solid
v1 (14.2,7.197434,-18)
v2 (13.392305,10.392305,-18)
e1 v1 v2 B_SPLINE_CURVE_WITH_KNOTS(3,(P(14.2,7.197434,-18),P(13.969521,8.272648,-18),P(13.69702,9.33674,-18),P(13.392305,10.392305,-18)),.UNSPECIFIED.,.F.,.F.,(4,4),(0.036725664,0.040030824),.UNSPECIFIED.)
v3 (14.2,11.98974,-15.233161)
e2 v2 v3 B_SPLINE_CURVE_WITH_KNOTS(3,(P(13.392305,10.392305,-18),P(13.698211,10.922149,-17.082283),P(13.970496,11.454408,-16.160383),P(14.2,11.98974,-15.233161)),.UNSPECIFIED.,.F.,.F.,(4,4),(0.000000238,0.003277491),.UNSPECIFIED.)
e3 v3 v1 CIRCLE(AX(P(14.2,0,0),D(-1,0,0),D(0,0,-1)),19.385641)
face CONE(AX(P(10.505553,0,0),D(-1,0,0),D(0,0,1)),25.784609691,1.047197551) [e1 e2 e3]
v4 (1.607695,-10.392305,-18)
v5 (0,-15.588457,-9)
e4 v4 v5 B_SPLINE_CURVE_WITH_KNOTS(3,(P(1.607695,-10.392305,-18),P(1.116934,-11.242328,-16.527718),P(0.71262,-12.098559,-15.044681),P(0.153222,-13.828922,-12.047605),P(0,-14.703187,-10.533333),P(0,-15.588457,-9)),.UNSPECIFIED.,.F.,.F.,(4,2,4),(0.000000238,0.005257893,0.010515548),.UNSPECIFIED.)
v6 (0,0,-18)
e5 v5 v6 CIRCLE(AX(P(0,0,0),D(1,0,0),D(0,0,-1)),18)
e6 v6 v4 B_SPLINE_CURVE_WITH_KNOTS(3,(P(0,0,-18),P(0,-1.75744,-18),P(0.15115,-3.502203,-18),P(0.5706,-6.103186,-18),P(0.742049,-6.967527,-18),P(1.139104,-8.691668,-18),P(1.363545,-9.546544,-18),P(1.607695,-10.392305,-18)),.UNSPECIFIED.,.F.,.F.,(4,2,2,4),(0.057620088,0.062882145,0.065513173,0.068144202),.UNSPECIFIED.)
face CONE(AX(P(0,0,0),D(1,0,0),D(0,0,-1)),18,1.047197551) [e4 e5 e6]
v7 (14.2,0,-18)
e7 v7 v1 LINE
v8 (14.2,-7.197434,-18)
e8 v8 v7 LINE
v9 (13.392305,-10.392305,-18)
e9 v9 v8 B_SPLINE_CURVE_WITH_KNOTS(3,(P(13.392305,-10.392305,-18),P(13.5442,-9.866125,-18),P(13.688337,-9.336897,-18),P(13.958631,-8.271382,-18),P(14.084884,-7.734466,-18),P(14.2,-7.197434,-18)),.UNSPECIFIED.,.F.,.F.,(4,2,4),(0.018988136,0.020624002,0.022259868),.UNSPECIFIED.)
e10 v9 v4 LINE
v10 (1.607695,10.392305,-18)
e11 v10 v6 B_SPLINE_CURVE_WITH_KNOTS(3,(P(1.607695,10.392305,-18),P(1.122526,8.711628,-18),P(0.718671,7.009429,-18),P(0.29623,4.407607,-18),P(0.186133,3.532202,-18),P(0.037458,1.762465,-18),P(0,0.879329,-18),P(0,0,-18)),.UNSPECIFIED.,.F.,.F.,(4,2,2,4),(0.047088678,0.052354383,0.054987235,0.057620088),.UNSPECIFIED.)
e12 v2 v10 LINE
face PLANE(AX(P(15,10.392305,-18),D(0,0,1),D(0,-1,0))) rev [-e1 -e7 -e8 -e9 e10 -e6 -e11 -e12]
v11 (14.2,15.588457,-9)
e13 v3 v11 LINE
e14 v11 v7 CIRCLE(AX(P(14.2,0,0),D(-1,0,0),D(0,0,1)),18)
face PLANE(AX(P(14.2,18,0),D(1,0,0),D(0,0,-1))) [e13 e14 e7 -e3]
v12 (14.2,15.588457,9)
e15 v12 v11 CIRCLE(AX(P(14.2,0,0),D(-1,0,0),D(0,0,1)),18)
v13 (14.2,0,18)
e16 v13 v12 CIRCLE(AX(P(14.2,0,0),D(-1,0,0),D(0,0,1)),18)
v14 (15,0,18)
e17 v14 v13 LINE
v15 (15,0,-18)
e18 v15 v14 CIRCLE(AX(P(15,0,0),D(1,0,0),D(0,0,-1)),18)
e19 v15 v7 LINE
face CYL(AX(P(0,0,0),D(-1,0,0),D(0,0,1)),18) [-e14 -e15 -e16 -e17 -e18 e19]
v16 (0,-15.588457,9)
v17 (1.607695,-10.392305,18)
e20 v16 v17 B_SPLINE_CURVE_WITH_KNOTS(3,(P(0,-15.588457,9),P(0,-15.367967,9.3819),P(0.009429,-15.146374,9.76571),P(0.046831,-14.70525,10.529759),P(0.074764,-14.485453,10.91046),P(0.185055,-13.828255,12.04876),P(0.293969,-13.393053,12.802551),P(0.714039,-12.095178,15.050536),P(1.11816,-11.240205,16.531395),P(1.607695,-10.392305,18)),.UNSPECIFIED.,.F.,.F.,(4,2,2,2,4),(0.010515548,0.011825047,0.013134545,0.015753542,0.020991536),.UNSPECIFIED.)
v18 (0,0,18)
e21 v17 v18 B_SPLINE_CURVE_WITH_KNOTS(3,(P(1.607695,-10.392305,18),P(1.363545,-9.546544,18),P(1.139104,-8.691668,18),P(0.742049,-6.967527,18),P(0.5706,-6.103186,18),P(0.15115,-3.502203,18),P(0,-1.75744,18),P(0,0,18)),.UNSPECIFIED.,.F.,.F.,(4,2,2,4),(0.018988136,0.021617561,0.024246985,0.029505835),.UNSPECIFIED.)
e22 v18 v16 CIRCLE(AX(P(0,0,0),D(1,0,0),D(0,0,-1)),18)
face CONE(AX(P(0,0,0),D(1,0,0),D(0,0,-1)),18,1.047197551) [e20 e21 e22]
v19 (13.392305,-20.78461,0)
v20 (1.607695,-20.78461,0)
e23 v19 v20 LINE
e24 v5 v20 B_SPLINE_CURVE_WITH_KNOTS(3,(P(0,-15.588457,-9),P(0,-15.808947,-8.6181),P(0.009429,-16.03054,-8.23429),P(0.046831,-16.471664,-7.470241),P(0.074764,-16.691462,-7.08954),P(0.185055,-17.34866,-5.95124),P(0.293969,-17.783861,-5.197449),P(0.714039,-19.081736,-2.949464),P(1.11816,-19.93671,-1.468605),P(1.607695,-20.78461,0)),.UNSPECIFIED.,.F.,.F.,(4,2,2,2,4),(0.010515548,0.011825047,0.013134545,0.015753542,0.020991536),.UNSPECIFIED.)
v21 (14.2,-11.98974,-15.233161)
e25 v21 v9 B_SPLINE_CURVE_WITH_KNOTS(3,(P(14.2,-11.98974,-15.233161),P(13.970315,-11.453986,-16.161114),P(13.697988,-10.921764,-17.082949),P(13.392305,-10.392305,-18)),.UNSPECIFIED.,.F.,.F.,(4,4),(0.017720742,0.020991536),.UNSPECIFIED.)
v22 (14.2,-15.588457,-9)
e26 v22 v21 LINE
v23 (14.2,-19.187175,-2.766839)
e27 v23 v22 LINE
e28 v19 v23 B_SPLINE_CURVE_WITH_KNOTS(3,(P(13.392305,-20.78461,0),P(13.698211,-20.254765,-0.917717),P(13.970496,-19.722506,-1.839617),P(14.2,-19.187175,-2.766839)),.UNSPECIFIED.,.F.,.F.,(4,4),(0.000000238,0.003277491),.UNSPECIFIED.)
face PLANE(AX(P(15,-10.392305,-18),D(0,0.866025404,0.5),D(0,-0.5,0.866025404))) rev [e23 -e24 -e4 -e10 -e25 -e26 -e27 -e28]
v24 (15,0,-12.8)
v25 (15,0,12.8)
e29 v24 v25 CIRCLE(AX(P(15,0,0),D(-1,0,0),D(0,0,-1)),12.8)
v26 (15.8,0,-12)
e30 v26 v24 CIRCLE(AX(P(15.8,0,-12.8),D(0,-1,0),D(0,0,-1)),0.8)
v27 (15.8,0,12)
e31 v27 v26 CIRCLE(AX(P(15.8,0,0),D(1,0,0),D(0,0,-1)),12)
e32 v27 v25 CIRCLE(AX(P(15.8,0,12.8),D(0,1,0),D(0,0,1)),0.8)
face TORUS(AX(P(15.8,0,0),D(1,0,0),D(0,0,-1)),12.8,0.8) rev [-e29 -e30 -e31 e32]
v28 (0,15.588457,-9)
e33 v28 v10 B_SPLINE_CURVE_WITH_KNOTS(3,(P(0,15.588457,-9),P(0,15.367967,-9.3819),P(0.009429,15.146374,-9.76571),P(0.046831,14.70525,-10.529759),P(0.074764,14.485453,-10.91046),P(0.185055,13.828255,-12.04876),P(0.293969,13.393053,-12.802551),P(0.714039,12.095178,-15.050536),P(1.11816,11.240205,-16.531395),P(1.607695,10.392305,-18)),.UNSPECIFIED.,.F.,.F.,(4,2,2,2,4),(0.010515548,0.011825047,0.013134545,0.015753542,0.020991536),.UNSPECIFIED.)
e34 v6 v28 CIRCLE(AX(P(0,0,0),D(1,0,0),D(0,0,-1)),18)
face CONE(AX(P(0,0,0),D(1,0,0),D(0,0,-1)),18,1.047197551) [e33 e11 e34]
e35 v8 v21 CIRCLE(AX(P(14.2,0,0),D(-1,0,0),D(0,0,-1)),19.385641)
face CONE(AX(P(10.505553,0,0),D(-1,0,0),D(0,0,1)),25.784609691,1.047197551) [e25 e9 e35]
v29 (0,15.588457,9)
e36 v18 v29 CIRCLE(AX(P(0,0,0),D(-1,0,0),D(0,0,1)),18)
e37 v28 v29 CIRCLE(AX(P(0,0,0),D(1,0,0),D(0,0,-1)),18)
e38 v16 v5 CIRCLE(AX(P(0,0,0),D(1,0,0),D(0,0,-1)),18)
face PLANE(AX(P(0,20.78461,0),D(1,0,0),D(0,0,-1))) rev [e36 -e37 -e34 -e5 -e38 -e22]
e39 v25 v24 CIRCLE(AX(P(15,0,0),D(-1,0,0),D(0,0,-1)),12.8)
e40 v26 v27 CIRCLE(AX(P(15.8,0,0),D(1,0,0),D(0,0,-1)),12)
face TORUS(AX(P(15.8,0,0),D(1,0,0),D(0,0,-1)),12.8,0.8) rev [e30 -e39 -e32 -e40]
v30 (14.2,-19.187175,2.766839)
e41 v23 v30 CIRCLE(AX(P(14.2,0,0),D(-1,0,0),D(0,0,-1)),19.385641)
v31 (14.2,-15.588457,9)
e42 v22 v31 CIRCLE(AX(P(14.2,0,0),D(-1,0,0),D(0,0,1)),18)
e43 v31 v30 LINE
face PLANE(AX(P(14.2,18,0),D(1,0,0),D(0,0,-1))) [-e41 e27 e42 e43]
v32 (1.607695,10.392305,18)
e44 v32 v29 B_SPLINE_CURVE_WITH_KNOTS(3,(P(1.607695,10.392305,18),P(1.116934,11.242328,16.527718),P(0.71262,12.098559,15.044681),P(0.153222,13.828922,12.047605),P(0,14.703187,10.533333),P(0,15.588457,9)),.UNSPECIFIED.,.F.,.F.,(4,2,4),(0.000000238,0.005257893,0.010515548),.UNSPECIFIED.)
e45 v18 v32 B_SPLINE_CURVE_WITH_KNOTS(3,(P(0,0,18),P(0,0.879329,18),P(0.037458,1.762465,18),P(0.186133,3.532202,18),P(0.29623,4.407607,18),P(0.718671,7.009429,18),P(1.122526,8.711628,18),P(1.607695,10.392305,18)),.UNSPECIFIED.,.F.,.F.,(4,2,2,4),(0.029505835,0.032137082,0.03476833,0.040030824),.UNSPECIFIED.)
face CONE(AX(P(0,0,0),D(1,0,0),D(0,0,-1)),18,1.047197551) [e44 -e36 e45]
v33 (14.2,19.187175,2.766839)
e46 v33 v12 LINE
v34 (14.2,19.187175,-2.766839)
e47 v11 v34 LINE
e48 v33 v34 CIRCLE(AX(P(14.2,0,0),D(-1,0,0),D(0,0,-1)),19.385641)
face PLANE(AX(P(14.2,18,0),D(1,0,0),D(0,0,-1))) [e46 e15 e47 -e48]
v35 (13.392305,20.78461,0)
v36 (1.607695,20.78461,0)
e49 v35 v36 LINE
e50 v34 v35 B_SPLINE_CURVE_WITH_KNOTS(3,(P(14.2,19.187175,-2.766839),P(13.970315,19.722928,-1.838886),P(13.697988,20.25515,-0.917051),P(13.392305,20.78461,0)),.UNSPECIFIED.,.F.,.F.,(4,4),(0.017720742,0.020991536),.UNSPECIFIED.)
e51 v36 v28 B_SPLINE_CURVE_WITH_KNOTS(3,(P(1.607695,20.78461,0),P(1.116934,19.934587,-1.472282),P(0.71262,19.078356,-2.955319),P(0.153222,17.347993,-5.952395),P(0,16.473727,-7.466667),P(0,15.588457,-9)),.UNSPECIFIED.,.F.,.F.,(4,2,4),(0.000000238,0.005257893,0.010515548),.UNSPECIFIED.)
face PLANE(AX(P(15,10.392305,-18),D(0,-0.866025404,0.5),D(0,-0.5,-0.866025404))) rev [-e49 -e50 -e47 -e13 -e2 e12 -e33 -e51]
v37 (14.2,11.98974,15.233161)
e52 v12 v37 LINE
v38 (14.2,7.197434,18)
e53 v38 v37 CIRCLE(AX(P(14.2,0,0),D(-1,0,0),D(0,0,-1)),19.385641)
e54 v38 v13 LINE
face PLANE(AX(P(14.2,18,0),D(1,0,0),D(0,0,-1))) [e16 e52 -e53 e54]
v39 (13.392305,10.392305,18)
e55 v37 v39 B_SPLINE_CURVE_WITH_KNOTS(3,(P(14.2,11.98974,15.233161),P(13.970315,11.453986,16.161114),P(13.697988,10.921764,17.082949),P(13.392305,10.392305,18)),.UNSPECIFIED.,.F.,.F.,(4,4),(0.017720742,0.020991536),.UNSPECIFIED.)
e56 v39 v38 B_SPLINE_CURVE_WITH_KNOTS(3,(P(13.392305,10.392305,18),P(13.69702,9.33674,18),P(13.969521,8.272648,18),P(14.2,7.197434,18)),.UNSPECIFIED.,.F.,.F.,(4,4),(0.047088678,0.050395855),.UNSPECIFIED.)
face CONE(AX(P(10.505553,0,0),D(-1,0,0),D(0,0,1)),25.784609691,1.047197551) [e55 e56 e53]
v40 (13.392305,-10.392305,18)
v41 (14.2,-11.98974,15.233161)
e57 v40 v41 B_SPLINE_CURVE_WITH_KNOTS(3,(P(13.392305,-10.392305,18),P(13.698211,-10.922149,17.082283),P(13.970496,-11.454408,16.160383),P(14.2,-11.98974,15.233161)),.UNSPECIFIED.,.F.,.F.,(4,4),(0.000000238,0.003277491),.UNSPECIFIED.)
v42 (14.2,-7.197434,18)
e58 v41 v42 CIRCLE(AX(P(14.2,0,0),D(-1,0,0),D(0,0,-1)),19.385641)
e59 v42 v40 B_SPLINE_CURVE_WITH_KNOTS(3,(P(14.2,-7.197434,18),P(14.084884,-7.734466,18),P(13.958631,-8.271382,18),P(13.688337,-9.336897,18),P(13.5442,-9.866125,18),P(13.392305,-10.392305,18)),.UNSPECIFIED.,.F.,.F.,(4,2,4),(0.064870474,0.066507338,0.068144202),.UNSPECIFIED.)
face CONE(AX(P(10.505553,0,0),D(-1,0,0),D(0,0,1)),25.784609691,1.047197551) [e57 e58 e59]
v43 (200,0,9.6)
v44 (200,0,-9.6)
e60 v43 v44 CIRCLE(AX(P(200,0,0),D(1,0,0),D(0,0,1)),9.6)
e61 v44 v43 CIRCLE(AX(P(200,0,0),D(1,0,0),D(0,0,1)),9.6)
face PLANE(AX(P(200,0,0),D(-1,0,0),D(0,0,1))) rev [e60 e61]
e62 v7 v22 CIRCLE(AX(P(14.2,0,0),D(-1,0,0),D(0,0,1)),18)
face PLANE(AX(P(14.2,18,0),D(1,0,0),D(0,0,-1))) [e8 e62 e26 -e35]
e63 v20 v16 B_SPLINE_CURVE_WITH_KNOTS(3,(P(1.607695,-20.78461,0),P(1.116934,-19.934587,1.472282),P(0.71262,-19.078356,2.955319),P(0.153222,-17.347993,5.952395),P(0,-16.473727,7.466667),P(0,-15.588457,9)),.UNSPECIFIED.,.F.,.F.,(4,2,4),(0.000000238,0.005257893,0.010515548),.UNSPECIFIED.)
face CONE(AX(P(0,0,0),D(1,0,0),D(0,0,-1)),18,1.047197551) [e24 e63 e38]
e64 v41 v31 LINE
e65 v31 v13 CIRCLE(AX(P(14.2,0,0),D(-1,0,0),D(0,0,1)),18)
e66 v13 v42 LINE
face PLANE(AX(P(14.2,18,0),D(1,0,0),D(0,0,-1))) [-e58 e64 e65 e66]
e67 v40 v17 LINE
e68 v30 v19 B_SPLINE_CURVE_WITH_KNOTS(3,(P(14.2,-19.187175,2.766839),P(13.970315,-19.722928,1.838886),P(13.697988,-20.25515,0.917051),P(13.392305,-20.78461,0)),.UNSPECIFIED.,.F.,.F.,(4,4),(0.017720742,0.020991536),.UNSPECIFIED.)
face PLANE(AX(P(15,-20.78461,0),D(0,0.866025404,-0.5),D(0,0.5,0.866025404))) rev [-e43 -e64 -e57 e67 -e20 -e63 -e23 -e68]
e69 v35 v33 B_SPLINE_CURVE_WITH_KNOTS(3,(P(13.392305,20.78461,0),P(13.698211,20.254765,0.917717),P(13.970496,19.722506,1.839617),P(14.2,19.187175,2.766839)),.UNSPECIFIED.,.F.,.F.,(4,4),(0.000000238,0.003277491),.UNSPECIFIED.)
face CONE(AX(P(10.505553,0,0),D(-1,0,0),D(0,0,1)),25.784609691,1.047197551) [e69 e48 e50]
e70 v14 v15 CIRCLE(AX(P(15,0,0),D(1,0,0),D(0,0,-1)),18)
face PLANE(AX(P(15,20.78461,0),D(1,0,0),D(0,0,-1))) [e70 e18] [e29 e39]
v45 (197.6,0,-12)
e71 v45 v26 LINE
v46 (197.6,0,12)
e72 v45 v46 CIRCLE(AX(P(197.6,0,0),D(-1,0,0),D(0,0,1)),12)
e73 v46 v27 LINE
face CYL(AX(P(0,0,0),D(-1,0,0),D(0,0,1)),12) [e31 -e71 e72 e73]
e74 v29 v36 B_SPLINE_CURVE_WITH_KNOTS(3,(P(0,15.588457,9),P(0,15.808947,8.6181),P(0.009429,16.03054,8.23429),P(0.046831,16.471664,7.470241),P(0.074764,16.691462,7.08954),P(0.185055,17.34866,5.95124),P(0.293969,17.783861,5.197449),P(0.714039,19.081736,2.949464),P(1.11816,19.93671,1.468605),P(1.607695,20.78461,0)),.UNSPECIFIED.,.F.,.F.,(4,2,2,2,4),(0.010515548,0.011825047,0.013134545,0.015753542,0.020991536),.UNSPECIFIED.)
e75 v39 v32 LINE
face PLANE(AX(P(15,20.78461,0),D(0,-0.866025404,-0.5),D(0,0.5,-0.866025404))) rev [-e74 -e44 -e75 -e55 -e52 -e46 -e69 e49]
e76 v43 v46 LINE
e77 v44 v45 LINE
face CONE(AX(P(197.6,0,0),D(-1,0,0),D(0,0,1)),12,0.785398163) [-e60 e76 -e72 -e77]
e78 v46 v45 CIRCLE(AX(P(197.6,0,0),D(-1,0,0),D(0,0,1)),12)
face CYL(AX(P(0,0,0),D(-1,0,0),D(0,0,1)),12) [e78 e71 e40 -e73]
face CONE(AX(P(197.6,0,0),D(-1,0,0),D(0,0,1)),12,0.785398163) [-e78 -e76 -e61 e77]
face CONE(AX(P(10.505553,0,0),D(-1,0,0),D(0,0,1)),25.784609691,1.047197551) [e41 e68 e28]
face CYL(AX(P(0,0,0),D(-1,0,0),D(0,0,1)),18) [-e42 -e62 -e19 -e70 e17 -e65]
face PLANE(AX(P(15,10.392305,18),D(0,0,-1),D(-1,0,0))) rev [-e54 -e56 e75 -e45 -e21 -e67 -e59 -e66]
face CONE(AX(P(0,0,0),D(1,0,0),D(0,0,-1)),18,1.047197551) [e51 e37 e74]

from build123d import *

# Parameters (mm, degrees)
BASE_EXTRUDE_DEPTH = 15
SKETCH4_W          = 0.8
SKETCH4_H          = 12.784609691
CHAMFER_2_SIZE     = 2.4
FILLET_2_R         = 0.8


with BuildPart() as part:
    # Sketch1 → Base-Extrude (new body)
    with BuildSketch(Plane(origin=(0, 0, 0), x_dir=(0, 0, -1), z_dir=(1, 0, 0))):
        Polygon((18, 10.392304845), (18, -10.392304845), (0, -20.784609691), (-18, -10.392304845), (-18, 10.392304845), (0, 20.784609691), align=None)
    extrude(amount=BASE_EXTRUDE_DEPTH)

    # Sketch2 → Boss-Revolve1 (revolve)
    with BuildSketch(Plane.XY, mode=Mode.PRIVATE) as boss_revolve1_sk:
        Polygon((0, 0), (200, 0), (200, 9.402), (200, 12), (27.8072, 12), (0, 12), align=None)
    revolve(boss_revolve1_sk.sketch.rotate(Axis((0, 0, 0), (1, 0, 0)), 90), axis=Axis((0, 0, 0), (1, 0, 0)))

    # Sketch3 → Cut-Revolve1 (revolve, cut)
    with BuildSketch(Plane.XY):
        Polygon((0, 18), (4.494446501, 25.784609691), (4.494446501, 30.784609691), (-10, 30.784609691), (-10, 18), align=None)
    revolve(axis=Axis((0, 0, 0), (1, 0, 0)), mode=Mode.SUBTRACT)

    # Sketch5 → Cut-Revolve2 (revolve, cut)
    with BuildSketch(Plane.XY):
        Polygon((15, 18), (10.505553499, 25.784609691), (10.505553499, 30.784609691), (20.505553499, 30.784609691), (20.505553499, 18), align=None)
    revolve(axis=Axis((0, 0, 0), (1, 0, 0)), mode=Mode.SUBTRACT)

    # Sketch4 → Cut-Revolve3 (revolve, cut)
    with BuildSketch(Plane.XY, mode=Mode.PRIVATE) as cut_revolve3_sk:
        with Locations((14.6, 24.392304845)):
            Rectangle(SKETCH4_W, SKETCH4_H)
    revolve(cut_revolve3_sk.sketch.rotate(Axis((0, 0, 0), (1, 0, 0)), 270), axis=Axis((0, 0, 0), (1, 0, 0)), mode=Mode.SUBTRACT)

    # Chamfer 2
    chamfer_2_edges = [part.edges().sort_by_distance(p)[0] for p in [
        (200, 0, -12),
    ]]
    chamfer(chamfer_2_edges, length=CHAMFER_2_SIZE)

    # Fillet 2
    fillet_2_edges = [part.edges().sort_by_distance(p)[0] for p in [
        (15, 0, -12),
    ]]
    fillet(fillet_2_edges, radius=FILLET_2_R)


solid = part.part
